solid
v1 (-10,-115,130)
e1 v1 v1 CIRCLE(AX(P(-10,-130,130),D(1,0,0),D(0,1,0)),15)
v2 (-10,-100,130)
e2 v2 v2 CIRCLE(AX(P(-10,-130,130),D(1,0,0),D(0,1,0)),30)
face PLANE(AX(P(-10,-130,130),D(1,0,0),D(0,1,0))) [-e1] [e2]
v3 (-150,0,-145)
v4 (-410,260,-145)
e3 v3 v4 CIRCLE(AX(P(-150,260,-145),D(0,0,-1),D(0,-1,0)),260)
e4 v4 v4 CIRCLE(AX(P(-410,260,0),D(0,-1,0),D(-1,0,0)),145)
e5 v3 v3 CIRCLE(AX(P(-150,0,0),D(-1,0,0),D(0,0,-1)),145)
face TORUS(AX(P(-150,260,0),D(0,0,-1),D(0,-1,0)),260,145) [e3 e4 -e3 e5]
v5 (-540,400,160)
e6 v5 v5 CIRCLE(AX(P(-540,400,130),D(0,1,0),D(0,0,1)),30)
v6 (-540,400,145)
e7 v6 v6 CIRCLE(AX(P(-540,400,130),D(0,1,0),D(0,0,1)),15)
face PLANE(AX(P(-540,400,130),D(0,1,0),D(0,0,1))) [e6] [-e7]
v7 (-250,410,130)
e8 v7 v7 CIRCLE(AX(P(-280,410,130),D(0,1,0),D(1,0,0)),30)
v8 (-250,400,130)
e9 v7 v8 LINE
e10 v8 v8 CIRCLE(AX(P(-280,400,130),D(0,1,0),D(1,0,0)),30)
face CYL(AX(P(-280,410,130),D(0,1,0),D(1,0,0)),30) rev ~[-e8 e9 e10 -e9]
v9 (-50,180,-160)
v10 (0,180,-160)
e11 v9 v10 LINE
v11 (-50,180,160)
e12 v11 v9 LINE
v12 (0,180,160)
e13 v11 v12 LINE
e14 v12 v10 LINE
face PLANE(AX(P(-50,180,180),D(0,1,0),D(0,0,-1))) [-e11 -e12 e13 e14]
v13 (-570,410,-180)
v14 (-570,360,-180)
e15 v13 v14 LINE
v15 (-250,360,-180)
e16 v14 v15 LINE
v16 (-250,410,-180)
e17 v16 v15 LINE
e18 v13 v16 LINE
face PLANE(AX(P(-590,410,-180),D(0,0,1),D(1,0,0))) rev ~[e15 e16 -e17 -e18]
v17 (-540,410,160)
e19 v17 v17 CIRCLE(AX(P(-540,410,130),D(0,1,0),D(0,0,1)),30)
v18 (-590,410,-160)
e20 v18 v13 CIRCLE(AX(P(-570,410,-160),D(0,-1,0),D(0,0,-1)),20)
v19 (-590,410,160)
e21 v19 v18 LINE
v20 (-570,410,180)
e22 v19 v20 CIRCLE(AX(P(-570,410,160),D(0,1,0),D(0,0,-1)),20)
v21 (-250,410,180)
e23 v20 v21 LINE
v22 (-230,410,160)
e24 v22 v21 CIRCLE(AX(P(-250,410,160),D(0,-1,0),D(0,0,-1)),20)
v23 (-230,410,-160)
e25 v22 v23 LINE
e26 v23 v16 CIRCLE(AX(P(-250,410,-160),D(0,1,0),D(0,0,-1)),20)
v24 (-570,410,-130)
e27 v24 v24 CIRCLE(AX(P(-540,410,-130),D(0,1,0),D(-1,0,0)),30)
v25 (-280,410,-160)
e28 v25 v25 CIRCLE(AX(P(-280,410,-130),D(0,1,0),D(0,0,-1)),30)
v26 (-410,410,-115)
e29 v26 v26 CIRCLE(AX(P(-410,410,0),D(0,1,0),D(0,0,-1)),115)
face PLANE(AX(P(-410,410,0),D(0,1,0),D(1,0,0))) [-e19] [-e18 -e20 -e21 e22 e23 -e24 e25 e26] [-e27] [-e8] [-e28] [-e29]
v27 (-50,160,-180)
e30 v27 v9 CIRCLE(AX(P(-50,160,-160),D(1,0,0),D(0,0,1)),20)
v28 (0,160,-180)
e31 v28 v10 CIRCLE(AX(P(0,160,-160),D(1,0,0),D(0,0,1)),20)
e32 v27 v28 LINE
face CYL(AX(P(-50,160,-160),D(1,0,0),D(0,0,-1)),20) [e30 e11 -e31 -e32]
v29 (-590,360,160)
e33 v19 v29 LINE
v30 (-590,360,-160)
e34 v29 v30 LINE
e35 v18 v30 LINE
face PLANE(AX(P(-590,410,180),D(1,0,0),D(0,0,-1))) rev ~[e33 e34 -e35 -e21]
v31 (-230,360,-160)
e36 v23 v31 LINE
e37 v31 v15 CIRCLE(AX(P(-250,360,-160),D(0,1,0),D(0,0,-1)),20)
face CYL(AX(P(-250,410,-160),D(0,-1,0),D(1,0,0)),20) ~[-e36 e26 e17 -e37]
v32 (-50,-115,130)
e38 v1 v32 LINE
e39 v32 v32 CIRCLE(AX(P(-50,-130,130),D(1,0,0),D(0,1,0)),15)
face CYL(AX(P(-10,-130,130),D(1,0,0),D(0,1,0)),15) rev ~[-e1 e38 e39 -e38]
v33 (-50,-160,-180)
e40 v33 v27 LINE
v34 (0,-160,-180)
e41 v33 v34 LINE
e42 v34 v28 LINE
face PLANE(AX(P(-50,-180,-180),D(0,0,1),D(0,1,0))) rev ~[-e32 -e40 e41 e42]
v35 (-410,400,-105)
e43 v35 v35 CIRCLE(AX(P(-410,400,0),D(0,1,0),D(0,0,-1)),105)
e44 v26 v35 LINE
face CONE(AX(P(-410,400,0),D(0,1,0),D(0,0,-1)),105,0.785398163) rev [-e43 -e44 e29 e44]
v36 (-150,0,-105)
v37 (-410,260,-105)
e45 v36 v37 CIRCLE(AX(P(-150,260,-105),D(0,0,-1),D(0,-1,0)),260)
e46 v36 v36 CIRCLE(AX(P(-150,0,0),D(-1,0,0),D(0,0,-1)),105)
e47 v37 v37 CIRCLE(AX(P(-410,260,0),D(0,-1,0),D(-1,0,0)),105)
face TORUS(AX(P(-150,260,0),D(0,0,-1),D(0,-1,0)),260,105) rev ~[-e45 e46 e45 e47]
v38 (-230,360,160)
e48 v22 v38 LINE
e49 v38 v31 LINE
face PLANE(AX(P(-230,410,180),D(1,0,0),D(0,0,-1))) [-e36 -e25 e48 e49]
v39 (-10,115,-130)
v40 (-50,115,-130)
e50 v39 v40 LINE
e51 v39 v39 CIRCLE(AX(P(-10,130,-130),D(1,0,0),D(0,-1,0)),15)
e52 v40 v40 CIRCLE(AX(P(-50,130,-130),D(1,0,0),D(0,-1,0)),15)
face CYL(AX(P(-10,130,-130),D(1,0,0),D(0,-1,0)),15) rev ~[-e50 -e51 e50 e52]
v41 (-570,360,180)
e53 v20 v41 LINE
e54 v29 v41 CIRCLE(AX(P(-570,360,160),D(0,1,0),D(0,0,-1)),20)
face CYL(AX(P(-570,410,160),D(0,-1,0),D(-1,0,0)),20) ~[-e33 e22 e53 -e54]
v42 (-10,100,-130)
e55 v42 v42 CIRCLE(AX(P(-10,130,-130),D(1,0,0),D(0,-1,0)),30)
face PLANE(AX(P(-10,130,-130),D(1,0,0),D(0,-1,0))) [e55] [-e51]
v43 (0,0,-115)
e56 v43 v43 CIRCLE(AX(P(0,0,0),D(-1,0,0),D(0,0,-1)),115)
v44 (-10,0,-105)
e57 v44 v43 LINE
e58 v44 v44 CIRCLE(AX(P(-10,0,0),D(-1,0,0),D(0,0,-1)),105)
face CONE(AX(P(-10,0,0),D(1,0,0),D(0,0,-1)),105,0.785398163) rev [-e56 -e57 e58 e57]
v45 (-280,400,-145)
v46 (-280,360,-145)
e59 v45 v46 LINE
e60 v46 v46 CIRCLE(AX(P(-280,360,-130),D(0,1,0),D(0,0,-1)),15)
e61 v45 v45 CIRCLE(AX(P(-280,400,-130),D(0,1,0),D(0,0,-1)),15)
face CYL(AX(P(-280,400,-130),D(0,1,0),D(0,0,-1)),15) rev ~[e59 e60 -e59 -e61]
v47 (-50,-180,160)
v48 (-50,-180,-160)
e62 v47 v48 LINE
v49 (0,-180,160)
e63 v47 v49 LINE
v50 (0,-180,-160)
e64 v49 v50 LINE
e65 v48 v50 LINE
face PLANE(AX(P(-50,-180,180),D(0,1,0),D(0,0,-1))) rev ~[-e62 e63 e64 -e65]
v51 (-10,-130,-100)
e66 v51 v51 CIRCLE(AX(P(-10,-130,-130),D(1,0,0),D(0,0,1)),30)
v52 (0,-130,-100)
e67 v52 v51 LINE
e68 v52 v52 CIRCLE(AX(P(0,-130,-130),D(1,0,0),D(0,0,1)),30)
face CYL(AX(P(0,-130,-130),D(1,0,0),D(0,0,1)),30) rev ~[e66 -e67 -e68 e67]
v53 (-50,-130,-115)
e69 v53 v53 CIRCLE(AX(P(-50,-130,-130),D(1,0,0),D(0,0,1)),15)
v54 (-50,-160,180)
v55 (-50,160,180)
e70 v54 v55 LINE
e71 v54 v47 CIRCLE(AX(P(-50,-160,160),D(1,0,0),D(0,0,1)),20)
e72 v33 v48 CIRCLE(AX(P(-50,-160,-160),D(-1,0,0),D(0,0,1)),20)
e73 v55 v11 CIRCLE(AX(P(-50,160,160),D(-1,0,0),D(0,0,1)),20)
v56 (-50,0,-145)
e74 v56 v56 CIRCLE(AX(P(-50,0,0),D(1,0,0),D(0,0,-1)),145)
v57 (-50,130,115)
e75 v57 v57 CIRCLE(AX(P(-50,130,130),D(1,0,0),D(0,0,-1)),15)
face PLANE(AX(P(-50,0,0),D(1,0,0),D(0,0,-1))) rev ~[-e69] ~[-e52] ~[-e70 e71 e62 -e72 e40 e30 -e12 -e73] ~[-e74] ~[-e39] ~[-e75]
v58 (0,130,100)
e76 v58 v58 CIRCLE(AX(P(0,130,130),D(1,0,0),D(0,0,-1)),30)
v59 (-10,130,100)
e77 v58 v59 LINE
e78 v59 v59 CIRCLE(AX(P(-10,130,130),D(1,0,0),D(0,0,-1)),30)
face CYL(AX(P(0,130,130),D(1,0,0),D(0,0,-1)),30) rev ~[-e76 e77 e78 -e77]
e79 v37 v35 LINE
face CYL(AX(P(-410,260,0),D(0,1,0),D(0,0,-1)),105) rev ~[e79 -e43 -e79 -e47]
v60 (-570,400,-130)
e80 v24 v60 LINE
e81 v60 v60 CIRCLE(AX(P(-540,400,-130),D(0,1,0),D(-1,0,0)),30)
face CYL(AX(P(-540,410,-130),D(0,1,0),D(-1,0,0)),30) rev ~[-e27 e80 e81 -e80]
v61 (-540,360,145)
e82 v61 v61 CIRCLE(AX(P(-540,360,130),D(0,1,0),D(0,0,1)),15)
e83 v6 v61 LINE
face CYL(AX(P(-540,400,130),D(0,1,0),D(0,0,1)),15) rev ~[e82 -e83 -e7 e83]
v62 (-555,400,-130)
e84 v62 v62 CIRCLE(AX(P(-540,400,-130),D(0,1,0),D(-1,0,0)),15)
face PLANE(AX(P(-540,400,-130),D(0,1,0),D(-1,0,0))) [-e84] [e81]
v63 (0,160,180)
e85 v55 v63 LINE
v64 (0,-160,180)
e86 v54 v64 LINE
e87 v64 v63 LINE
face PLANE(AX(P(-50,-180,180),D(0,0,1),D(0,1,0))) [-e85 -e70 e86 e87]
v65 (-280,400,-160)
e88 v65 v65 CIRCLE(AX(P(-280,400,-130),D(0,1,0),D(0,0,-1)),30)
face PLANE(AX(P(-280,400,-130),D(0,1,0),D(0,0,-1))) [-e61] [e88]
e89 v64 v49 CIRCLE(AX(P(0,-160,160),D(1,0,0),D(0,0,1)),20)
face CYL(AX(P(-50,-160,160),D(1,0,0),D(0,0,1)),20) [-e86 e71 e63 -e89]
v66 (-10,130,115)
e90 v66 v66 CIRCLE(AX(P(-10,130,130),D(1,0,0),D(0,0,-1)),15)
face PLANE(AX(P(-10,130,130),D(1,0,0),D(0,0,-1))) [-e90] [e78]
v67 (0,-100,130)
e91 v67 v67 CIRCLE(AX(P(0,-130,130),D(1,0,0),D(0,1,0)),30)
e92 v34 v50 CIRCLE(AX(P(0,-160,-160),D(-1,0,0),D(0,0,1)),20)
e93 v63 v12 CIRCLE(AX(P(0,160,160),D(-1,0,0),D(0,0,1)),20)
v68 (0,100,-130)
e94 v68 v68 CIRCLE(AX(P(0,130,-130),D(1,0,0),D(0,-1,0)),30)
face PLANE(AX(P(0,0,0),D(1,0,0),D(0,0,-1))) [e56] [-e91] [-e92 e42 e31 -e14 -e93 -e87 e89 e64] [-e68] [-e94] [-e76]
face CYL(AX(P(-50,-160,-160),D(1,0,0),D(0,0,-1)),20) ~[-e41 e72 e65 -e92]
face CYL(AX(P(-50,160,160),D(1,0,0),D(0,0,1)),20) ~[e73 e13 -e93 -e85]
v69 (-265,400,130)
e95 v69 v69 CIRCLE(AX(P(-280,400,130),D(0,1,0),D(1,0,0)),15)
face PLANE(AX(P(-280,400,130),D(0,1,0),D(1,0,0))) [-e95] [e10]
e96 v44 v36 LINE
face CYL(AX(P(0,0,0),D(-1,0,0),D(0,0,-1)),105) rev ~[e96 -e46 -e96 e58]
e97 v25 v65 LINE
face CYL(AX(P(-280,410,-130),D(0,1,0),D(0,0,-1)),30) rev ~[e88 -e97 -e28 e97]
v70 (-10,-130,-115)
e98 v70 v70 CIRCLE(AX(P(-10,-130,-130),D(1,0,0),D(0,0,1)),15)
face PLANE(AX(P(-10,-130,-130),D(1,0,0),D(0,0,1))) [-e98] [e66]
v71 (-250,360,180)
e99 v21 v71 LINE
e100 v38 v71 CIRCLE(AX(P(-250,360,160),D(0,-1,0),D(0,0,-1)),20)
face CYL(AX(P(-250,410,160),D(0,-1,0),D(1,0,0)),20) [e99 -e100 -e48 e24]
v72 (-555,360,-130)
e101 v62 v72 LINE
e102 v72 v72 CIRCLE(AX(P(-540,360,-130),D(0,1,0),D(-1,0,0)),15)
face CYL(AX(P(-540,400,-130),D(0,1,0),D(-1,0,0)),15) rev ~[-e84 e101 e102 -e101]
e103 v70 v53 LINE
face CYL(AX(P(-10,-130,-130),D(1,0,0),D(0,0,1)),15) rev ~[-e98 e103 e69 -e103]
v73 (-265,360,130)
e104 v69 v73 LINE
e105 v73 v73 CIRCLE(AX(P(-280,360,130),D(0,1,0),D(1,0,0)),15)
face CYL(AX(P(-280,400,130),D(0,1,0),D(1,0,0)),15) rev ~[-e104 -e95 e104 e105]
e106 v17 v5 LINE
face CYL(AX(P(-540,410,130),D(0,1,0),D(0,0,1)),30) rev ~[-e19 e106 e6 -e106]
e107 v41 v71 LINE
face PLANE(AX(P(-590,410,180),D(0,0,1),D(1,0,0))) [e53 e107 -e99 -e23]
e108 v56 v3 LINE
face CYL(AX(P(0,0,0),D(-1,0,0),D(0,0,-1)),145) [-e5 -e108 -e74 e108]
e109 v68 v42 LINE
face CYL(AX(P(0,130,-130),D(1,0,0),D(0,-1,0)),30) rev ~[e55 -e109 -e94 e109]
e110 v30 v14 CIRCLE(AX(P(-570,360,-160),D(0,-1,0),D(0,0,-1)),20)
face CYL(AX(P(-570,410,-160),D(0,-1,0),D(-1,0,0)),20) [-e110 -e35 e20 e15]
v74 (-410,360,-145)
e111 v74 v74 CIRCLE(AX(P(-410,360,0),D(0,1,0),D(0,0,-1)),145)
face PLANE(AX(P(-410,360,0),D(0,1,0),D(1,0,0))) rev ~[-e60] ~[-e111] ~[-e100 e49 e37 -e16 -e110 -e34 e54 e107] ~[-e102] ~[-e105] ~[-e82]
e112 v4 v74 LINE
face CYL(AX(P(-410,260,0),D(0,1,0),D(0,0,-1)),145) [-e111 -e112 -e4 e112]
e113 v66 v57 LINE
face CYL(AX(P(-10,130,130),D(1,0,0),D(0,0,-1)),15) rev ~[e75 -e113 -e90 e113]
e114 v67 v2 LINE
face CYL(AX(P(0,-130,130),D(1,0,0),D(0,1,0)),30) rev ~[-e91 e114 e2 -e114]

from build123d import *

# Parameters (mm, degrees)
PIPE_PROFILE_SKETCH_290_R           = 145
PIPE_PROFILE_SKETCH_290_R_2         = 105
FLANGE_START                        = -50
FLANGE_A_SKETCH_360X360_W           = 360
FLANGE_A_SKETCH_360X360_H           = 360
FLANGE_A_SKETCH_360X360_R           = 145
FLANGE_A_360X360X50_DEPTH           = 50
FLANGE_A_CORNER_FILLETS_R20_R       = 20
FLANGE_B_SKETCH_360X360_W           = 360
FLANGE_B_SKETCH_360X360_H           = 360
FLANGE_B_SKETCH_360X360_R           = 145
FLANGE_B_360X360X50_DEPTH           = 50
FLANGE_B_CORNER_FILLETS_R20_R       = 20
FLANGE_A_COUNTERBORE_SKETCH_60_R    = 30
FLANGE_A_COUNTERBORE_60X10_DEPTH    = 10
FLANGE_A_BOLT_HOLE_30_REACH         = 734.735
FLANGE_A_BOLT_HOLE_SKETCH_30_R      = 15
FLANGE_A_BOLT_HOLE_PATTERN_4X_COUNT = 4
FLANGE_B_COUNTERBORE_SKETCH_60_R    = 30
FLANGE_B_COUNTERBORE_60X10_DEPTH    = 10
FLANGE_B_BOLT_HOLE_30_REACH         = 848.699
FLANGE_B_BOLT_HOLE_SKETCH_30_R      = 15
FLANGE_B_BOLT_HOLE_PATTERN_4X_COUNT = 4
PIPE_EDGE_CHAMFER_10X45DEG_SIZE     = 10


with BuildPart() as part:
    # Elbow Pipe Sweep Wall 40: sweep along a path in Elbow Path Sketch
    with BuildLine(Plane.XY) as elbow_pipe_sweep_wall_40_path:
        Line((0, 0), (-150, 0))
        ThreePointArc((-150, 0), (-333.847763109, 76.152236891), (-410, 260))
        Line((-410, 260), (-410, 410))
    # Pipe Profile Sketch Ø290 → Elbow Pipe Sweep Wall 40 (sweep)
    with BuildSketch(Plane(origin=(0, 0, 0), x_dir=(0, 0, -1), z_dir=(1, 0, 0))):
        Circle(PIPE_PROFILE_SKETCH_290_R)
        Circle(PIPE_PROFILE_SKETCH_290_R_2, mode=Mode.SUBTRACT)
    sweep(path=elbow_pipe_sweep_wall_40_path.line)

    # Flange A Sketch 360x360 → Flange A 360x360x50 (add)
    with BuildSketch(Plane(origin=(0, 0, 0), x_dir=(0, 0, -1), z_dir=(1, 0, 0)).offset(FLANGE_START)):
        Rectangle(FLANGE_A_SKETCH_360X360_W, FLANGE_A_SKETCH_360X360_H)
        with Locations(Location((0, 0, 0), (0, 0, 270))):
            Circle(FLANGE_A_SKETCH_360X360_R, mode=Mode.SUBTRACT)
    extrude(amount=FLANGE_A_360X360X50_DEPTH)

    # Flange A Corner Fillets R20
    flange_a_corner_fillets_r20_edges = [part.edges().sort_by_distance(p)[0] for p in [
        (-25, 180, -180),
        (-25, -180, -180),
        (-25, -180, 180),
        (-25, 180, 180),
    ]]
    fillet(flange_a_corner_fillets_r20_edges, radius=FLANGE_A_CORNER_FILLETS_R20_R)

    # Flange B Sketch 360x360 → Flange B 360x360x50 (add)
    with BuildSketch(Plane(origin=(0, 410, 0), x_dir=(1, 0, 0), z_dir=(0, 1, 0))):
        with Locations((-410, 0)):
            Rectangle(FLANGE_B_SKETCH_360X360_W, FLANGE_B_SKETCH_360X360_H)
        with Locations(Location((-410, 0, 0), (0, 0, 180))):
            Circle(FLANGE_B_SKETCH_360X360_R, mode=Mode.SUBTRACT)
    extrude(amount=-FLANGE_B_360X360X50_DEPTH)

    # Flange B Corner Fillets R20
    flange_b_corner_fillets_r20_edges = [part.edges().sort_by_distance(p)[0] for p in [
        (-230, 385, -180),
        (-230, 385, 180),
        (-590, 385, 180),
        (-590, 385, -180),
    ]]
    fillet(flange_b_corner_fillets_r20_edges, radius=FLANGE_B_CORNER_FILLETS_R20_R)

    # Flange A Counterbore Sketch Ø60 → Flange A Counterbore Ø60x10 (cut)
    with BuildSketch(Plane(origin=(0, 0, 0), x_dir=(0, 0, -1), z_dir=(1, 0, 0))):
        with Locations((-130, 130)):
            Circle(FLANGE_A_COUNTERBORE_SKETCH_60_R)
    flange_a_counterbore_60x10 = extrude(amount=-FLANGE_A_COUNTERBORE_60X10_DEPTH, mode=Mode.SUBTRACT)

    # Flange A Bolt Hole Sketch Ø30 → Flange A Bolt Hole Ø30 (cut, up to next)
    with BuildSketch(Plane(origin=(-10, 0, 0), x_dir=(0, 0, -1), z_dir=(1, 0, 0)), mode=Mode.PRIVATE) as flange_a_bolt_hole_30_sk1:
        with Locations((-130, 130)):
            Circle(FLANGE_A_BOLT_HOLE_SKETCH_30_R)
    flange_a_bolt_hole_30_tool1 = extrude(flange_a_bolt_hole_30_sk1.sketch, amount=-FLANGE_A_BOLT_HOLE_30_REACH, mode=Mode.PRIVATE) & part.part
    flange_a_bolt_hole_30 = flange_a_bolt_hole_30_tool1.solids().sort_by_distance((-10, 130, 130))[0]
    add(flange_a_bolt_hole_30, mode=Mode.SUBTRACT)

    # Flange A Bolt Hole Pattern 4x: Flange A Counterbore Ø60x10, Flange A Bolt Hole Ø30 ×4 about axis
    flange_a_bolt_hole_pattern_4x_axis = Axis((0, 0, 0), (1, 0, 0))
    add([flange_a_counterbore_60x10.rotate(flange_a_bolt_hole_pattern_4x_axis, i * 360 / FLANGE_A_BOLT_HOLE_PATTERN_4X_COUNT) for i in range(1, FLANGE_A_BOLT_HOLE_PATTERN_4X_COUNT)], mode=Mode.SUBTRACT)
    add([flange_a_bolt_hole_30.rotate(flange_a_bolt_hole_pattern_4x_axis, i * 360 / FLANGE_A_BOLT_HOLE_PATTERN_4X_COUNT) for i in range(1, FLANGE_A_BOLT_HOLE_PATTERN_4X_COUNT)], mode=Mode.SUBTRACT)

    # Flange B Counterbore Sketch Ø60 → Flange B Counterbore Ø60x10 (cut)
    with BuildSketch(Plane(origin=(0, 410, 0), x_dir=(1, 0, 0), z_dir=(0, 1, 0))):
        with Locations(Location((-540, 130, 0), (0, 0, 180))):
            Circle(FLANGE_B_COUNTERBORE_SKETCH_60_R)
    flange_b_counterbore_60x10 = extrude(amount=-FLANGE_B_COUNTERBORE_60X10_DEPTH, mode=Mode.SUBTRACT)

    # Flange B Bolt Hole Sketch Ø30 → Flange B Bolt Hole Ø30 (cut, up to next)
    with BuildSketch(Plane(origin=(0, 400, 0), x_dir=(1, 0, 0), z_dir=(0, 1, 0)), mode=Mode.PRIVATE) as flange_b_bolt_hole_30_sk1:
        with Locations(Location((-540, 130, 0), (0, 0, 180))):
            Circle(FLANGE_B_BOLT_HOLE_SKETCH_30_R)
    flange_b_bolt_hole_30_tool1 = extrude(flange_b_bolt_hole_30_sk1.sketch, amount=-FLANGE_B_BOLT_HOLE_30_REACH, mode=Mode.PRIVATE) & part.part
    flange_b_bolt_hole_30 = flange_b_bolt_hole_30_tool1.solids().sort_by_distance((-540, 400, -130))[0]
    add(flange_b_bolt_hole_30, mode=Mode.SUBTRACT)

    # Flange B Bolt Hole Pattern 4x: Flange B Counterbore Ø60x10, Flange B Bolt Hole Ø30 ×4 about axis
    flange_b_bolt_hole_pattern_4x_axis = Axis((-410, 0, 0), (0, 1, 0))
    add([flange_b_counterbore_60x10.rotate(flange_b_bolt_hole_pattern_4x_axis, i * 360 / FLANGE_B_BOLT_HOLE_PATTERN_4X_COUNT) for i in range(1, FLANGE_B_BOLT_HOLE_PATTERN_4X_COUNT)], mode=Mode.SUBTRACT)
    add([flange_b_bolt_hole_30.rotate(flange_b_bolt_hole_pattern_4x_axis, i * 360 / FLANGE_B_BOLT_HOLE_PATTERN_4X_COUNT) for i in range(1, FLANGE_B_BOLT_HOLE_PATTERN_4X_COUNT)], mode=Mode.SUBTRACT)

    # Pipe Edge Chamfer 10x45deg
    pipe_edge_chamfer_10x45deg_edges = [part.edges().sort_by_distance(p)[0] for p in [
        (0, 0, 105),
        (-410, 410, 105),
    ]]
    chamfer(pipe_edge_chamfer_10x45deg_edges, length=PIPE_EDGE_CHAMFER_10X45DEG_SIZE)


solid = part.part
